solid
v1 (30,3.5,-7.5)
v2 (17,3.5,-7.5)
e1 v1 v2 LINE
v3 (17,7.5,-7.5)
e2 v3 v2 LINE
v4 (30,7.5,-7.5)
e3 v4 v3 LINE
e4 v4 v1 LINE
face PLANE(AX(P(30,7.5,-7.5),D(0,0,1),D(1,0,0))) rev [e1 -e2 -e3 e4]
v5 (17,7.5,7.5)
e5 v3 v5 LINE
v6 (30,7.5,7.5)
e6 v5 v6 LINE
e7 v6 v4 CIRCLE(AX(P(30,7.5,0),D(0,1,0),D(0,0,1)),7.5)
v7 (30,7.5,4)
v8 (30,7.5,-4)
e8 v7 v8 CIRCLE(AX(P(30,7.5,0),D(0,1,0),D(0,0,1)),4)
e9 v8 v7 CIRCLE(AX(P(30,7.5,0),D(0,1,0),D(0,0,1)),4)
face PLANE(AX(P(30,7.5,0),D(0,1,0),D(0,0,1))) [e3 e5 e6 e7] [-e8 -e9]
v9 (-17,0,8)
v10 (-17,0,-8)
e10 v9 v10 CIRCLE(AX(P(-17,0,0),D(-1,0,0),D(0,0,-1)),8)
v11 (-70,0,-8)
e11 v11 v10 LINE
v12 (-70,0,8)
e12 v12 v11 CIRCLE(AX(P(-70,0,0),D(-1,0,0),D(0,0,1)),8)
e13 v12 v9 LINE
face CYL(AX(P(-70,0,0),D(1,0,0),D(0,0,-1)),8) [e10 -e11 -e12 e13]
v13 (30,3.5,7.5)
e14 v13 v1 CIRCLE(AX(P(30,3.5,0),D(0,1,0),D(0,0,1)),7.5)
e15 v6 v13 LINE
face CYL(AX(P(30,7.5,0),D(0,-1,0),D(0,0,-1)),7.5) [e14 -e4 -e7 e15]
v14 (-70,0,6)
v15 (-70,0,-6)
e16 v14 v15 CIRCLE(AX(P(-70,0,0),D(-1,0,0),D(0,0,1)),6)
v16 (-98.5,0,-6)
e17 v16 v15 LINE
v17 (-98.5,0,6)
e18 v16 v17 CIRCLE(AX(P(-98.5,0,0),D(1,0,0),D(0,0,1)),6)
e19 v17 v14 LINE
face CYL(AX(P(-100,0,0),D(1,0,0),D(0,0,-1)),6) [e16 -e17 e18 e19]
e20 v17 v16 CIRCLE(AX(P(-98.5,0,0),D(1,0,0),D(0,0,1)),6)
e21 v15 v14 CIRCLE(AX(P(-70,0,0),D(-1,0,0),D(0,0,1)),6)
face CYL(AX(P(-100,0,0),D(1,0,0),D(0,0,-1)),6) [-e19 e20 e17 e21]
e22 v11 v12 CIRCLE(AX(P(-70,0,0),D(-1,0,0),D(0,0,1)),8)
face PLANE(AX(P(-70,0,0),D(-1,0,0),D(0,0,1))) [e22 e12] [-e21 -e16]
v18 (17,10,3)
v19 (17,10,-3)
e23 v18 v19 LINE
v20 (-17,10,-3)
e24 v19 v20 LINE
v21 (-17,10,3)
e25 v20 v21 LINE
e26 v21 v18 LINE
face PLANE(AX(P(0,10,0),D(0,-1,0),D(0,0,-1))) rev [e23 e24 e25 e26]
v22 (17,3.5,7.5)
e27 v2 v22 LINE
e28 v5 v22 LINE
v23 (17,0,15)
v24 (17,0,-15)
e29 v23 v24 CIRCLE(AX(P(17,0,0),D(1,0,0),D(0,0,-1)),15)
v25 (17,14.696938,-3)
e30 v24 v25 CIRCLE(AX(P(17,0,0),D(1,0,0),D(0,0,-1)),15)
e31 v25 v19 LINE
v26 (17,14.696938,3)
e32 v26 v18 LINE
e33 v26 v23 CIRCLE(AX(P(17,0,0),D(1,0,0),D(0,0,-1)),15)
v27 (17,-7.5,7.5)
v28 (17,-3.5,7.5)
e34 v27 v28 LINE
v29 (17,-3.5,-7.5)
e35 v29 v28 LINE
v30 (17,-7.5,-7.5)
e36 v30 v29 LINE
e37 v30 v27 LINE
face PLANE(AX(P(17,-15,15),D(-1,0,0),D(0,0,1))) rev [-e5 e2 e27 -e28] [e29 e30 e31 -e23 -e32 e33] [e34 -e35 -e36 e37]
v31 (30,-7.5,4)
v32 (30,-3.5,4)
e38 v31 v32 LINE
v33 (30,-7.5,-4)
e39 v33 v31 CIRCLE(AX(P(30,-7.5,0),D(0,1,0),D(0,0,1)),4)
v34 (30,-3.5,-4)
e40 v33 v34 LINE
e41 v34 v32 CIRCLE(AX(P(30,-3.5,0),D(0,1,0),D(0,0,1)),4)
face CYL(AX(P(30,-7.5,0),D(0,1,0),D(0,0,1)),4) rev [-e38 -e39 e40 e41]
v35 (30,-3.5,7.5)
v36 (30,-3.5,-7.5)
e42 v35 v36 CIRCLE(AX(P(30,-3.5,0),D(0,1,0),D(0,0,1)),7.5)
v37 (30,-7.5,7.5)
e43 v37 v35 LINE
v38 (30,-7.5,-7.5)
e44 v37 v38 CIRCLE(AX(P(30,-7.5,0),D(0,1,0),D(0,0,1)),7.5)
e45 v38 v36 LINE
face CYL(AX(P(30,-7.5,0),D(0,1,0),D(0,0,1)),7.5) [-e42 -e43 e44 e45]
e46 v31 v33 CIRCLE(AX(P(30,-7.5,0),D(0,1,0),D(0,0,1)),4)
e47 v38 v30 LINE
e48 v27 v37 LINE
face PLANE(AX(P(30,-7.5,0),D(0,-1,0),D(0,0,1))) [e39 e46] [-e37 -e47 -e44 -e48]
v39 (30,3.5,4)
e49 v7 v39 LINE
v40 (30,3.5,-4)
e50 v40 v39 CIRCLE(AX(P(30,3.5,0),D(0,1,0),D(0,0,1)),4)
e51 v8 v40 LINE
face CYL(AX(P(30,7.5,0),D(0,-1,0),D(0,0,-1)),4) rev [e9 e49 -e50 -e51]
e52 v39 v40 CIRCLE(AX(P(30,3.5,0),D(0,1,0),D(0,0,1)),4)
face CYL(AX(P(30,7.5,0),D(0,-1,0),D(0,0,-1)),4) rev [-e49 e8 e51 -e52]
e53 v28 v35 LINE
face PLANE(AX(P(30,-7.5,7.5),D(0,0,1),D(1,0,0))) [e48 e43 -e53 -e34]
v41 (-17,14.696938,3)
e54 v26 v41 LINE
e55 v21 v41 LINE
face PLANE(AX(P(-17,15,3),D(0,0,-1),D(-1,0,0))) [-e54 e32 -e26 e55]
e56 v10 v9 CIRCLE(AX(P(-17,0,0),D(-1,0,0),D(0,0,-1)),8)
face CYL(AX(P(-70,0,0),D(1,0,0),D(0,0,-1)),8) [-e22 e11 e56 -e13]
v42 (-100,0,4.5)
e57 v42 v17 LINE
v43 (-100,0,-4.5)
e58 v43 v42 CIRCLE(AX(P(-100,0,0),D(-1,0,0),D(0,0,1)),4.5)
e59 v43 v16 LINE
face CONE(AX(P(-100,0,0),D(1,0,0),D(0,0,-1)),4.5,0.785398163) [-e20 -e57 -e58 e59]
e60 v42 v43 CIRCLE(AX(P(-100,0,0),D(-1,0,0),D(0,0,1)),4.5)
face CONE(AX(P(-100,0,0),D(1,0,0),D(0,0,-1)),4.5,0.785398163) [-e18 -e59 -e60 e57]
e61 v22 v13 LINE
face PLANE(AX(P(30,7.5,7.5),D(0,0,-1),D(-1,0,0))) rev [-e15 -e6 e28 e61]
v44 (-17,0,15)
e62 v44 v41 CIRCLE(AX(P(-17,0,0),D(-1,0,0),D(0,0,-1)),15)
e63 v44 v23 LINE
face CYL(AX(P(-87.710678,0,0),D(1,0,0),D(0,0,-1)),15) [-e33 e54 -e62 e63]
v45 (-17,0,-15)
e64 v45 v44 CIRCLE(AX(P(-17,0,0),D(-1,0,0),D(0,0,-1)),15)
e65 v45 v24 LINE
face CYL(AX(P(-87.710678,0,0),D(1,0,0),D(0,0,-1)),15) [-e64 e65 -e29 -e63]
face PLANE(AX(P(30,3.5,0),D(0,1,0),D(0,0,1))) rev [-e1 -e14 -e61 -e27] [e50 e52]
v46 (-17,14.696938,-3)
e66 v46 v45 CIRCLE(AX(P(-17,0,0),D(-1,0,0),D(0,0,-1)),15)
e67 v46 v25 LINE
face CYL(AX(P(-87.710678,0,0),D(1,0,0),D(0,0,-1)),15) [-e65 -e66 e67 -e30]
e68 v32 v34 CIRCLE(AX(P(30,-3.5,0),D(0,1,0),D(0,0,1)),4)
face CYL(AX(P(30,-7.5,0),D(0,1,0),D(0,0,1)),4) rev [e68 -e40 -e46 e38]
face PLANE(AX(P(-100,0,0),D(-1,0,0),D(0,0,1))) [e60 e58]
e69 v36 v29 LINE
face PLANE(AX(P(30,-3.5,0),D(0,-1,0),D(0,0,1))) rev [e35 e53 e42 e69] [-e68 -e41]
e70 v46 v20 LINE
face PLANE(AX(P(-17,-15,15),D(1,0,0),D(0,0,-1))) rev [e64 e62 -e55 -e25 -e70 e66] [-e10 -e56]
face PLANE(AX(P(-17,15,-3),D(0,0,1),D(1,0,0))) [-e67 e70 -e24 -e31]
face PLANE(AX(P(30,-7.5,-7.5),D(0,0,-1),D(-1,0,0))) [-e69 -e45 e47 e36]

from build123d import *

# Parameters (mm, degrees)
SKETCH_1_W          = 34
SKETCH_1_H          = 30
EXTRUDE_1_DEPTH     = 15
SKETCH_6_R          = 25
SKETCH_6_R_2        = 15
CUT_EXTRUDE_2_DEPTH = 34
CUT_EXTRUDE_START   = 10
SKETCH_2_W          = 34
SKETCH_2_H          = 6
CUT_EXTRUDE_1_DEPTH = 18.184554438
SKETCH_3_R          = 8
EXTRUDE_2_DEPTH     = 53
SKETCH_4_R          = 6
EXTRUDE_3_DEPTH     = 30
CHAMFER_1_SIZE      = 1.5
EXTRUDE_START       = 3.5
SKETCH_5_R          = 4
EXTRUDE_4_DEPTH     = 4


with BuildPart() as part:
    # 草图1 → 凸台-拉伸1 (new, symmetric)
    with BuildSketch(Plane.XY):
        Rectangle(SKETCH_1_W, SKETCH_1_H)
    extrude(amount=EXTRUDE_1_DEPTH, both=True)

    # 草图6 → 切除-拉伸2 (cut)
    with BuildSketch(Plane(origin=(17, 0, 0), x_dir=(0, 0, -1), z_dir=(1, 0, 0))):
        Circle(SKETCH_6_R)
        Circle(SKETCH_6_R_2, mode=Mode.SUBTRACT)
    extrude(amount=-CUT_EXTRUDE_2_DEPTH, mode=Mode.SUBTRACT)

    # 草图2 → 切除-拉伸1 (cut, through all)
    with BuildSketch(Plane(origin=(0, 0, 0), x_dir=(1, 0, 0), z_dir=(0, 1, 0)).offset(CUT_EXTRUDE_START)):
        Rectangle(SKETCH_2_W, SKETCH_2_H)
    extrude(amount=CUT_EXTRUDE_1_DEPTH, mode=Mode.SUBTRACT)

    # 草图3 → 凸台-拉伸2 (add)
    with BuildSketch(Plane.ZY.offset(17)):
        with Locations(Location((0, 0, 0), (0, 0, 180))):
            Circle(SKETCH_3_R)
    extrude(amount=EXTRUDE_2_DEPTH)

    # 草图4 → 凸台-拉伸3 (add)
    with BuildSketch(Plane.ZY.offset(70)):
        Circle(SKETCH_4_R)
    extrude(amount=EXTRUDE_3_DEPTH)

    # 倒角1
    chamfer_1_edges = [part.edges().sort_by_distance(p)[0] for p in [
        (-100, 0, -6),
    ]]
    chamfer(chamfer_1_edges, length=CHAMFER_1_SIZE)

    # 草图5 → 凸台-拉伸4 (add)
    with BuildSketch(Plane(origin=(0, 0, 0), x_dir=(1, 0, 0), z_dir=(0, 1, 0)).offset(EXTRUDE_START)):
        with BuildLine():
            Line((30, -7.5), (17, -7.5))
            Line((17, -7.5), (17, 7.5))
            Line((17, 7.5), (30, 7.5))
            ThreePointArc((30, 7.5), (37.5, 0), (30, -7.5))
        make_face()
        with Locations(Location((30, 0, 0), (0, 0, 270))):
            Circle(SKETCH_5_R, mode=Mode.SUBTRACT)
    extrude_4 = extrude(amount=EXTRUDE_4_DEPTH)

    # 镜向1: 凸台-拉伸4 across plane
    add(extrude_4.mirror(Plane.ZX))


solid = part.part
